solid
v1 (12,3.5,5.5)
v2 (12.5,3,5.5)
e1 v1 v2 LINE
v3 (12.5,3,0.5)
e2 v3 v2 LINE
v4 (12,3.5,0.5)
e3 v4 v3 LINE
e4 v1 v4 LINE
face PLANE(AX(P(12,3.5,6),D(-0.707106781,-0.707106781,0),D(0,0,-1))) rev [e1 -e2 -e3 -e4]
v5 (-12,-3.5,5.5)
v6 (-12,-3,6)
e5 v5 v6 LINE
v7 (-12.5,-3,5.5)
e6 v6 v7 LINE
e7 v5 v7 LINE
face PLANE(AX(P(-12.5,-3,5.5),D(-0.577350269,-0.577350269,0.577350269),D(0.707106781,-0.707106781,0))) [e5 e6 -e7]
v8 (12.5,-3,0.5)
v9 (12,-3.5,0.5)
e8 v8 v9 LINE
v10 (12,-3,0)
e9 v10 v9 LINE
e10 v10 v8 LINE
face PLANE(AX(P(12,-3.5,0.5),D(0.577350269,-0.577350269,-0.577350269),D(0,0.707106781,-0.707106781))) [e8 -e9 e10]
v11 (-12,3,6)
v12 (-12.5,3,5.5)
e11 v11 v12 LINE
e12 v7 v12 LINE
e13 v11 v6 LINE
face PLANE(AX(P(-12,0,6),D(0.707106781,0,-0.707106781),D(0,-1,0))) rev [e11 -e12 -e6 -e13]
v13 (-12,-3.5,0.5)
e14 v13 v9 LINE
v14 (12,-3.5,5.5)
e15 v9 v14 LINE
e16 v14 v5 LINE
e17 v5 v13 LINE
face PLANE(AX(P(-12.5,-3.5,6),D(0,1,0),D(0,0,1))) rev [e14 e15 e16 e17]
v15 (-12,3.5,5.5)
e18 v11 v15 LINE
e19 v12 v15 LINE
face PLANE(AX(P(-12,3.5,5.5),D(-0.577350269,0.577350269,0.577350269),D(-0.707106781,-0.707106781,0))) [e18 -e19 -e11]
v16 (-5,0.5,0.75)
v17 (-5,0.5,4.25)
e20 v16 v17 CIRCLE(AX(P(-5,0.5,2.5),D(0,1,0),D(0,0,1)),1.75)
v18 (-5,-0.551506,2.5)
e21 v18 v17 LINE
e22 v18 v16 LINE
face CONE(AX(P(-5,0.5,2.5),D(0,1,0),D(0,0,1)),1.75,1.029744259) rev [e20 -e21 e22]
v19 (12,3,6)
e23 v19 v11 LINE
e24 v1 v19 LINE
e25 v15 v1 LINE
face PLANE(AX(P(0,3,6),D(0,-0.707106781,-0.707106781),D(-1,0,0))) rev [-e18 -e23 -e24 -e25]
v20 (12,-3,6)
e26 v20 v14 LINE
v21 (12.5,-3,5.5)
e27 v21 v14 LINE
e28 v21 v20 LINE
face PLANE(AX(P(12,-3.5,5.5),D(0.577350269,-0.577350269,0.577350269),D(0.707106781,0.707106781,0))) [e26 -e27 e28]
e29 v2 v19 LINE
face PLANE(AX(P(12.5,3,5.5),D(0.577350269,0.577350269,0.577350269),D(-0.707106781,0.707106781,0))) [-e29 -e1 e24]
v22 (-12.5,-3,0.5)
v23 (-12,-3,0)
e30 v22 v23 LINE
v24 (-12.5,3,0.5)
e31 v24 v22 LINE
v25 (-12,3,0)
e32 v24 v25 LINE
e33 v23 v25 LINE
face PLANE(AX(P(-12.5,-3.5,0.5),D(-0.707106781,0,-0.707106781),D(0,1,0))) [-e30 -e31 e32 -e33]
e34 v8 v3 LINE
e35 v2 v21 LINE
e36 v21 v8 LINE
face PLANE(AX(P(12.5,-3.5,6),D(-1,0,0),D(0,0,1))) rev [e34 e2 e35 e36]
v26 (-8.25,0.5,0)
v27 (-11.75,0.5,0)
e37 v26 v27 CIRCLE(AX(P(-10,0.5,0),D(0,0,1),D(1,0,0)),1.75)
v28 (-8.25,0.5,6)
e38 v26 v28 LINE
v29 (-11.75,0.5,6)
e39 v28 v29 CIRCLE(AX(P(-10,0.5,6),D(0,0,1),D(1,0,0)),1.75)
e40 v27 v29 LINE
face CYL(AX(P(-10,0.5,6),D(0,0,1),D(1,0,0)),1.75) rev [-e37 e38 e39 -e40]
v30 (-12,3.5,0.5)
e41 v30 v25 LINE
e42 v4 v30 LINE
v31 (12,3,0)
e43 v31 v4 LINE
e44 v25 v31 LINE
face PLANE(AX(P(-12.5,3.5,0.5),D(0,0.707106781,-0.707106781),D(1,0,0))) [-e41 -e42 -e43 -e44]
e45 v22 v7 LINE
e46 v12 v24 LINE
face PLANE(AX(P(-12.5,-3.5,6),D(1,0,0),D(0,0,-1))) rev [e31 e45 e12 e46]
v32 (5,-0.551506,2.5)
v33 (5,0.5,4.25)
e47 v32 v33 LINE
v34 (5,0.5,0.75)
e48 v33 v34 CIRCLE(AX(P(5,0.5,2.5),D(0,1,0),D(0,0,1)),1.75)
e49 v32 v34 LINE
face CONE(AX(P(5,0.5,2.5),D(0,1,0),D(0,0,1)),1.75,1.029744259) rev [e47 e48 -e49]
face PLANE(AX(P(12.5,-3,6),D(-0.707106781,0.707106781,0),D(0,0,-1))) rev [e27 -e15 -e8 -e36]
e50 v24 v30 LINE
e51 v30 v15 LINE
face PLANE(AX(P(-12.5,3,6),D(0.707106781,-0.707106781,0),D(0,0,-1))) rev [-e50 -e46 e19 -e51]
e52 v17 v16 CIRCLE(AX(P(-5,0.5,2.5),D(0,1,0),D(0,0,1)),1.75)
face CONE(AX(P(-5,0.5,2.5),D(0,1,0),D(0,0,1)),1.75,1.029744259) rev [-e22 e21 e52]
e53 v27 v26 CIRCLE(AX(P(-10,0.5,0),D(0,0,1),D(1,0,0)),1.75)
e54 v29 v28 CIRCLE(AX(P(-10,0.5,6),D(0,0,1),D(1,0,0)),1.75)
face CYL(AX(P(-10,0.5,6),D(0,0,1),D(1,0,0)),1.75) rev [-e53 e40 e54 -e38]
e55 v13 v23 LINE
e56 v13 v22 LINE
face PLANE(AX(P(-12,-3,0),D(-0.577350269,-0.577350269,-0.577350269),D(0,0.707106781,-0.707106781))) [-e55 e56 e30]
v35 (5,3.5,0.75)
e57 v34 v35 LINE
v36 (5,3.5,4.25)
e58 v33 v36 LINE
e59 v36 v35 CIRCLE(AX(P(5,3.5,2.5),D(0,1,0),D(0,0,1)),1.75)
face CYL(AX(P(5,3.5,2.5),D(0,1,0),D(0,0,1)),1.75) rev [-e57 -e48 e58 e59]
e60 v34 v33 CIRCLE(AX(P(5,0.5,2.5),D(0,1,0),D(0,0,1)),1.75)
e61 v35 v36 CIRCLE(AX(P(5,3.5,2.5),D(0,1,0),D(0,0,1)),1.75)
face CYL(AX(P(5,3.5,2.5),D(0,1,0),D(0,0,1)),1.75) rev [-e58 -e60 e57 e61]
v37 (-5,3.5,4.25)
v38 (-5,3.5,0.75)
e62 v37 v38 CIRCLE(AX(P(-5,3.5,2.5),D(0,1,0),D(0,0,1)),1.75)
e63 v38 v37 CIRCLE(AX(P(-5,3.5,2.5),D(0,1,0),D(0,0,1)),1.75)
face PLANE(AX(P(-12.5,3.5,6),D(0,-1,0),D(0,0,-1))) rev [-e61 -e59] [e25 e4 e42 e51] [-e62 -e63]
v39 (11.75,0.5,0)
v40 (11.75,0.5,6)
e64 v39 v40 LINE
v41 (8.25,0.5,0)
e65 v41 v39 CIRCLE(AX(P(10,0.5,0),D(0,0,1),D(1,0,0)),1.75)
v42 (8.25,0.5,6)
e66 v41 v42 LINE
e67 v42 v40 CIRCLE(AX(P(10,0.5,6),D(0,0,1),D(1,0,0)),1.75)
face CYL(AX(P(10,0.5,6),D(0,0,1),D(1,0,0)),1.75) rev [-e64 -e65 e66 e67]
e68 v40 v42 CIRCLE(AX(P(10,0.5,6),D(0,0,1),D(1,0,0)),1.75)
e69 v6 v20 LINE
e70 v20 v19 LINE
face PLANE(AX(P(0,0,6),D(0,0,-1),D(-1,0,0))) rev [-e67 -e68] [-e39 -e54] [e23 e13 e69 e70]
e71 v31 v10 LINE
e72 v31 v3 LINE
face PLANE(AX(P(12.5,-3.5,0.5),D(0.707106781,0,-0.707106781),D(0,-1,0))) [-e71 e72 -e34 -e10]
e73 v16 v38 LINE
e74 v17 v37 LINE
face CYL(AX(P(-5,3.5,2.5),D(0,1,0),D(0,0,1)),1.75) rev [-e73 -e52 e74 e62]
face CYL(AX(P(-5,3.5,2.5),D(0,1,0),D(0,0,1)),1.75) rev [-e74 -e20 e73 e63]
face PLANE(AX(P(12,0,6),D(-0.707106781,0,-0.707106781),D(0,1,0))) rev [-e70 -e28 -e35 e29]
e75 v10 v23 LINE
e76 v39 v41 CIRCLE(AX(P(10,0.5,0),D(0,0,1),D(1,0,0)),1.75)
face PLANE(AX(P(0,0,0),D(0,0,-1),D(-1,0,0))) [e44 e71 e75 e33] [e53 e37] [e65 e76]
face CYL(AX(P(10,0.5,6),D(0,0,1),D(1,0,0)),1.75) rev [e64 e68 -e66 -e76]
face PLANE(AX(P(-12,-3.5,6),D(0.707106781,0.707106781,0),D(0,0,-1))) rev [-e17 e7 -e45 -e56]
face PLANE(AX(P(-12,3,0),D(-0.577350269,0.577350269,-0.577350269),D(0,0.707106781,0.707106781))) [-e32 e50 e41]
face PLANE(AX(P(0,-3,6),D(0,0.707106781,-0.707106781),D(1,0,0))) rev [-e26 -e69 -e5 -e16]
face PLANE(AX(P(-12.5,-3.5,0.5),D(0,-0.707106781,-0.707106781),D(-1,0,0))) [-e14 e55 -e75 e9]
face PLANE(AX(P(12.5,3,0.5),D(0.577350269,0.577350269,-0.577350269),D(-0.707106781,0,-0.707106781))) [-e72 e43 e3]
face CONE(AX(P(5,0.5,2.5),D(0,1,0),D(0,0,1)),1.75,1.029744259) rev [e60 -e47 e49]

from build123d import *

# Parameters (mm, degrees)
SKETCH1_W                      = 25
SKETCH1_H                      = 7
BOSS_EXTRUDE1_DEPTH            = 6
F_3_5_3_5_DIAMETER_HOLE2_D     = 3.5
F_3_5_3_5_DIAMETER_HOLE3_D     = 3.5
F_3_5_3_5_DIAMETER_HOLE3_DEPTH = 3
F_3_5_3_5_DIAMETER_HOLE3_TIP   = 1.051506083
CHAMFER1_SIZE                  = 0.5


with BuildPart() as part:
    # Sketch1 → Boss-Extrude1 (new body)
    with BuildSketch(Plane.XY):
        Rectangle(SKETCH1_W, SKETCH1_H)
    extrude(amount=BOSS_EXTRUDE1_DEPTH)

    # Ø3.5 (3.5) Diameter Hole2 (through all)
    with Locations(Plane.XY.offset(6)):
        with Locations((-10, 0.5), (10, 0.5)):
            Hole(F_3_5_3_5_DIAMETER_HOLE2_D / 2)

    # Ø3.5 (3.5) Diameter Hole3
    with Locations(Plane(origin=(0, 3.5, 0), x_dir=(1, 0, 0), z_dir=(0, 1, 0))):
        with Locations((5, -2.5), (-5, -2.5)):
            Hole(F_3_5_3_5_DIAMETER_HOLE3_D / 2, depth=F_3_5_3_5_DIAMETER_HOLE3_DEPTH)
            with Locations((0, 0, -(F_3_5_3_5_DIAMETER_HOLE3_DEPTH + F_3_5_3_5_DIAMETER_HOLE3_TIP / 2))):  # 118° drill point
                Cone(0, F_3_5_3_5_DIAMETER_HOLE3_D / 2, F_3_5_3_5_DIAMETER_HOLE3_TIP, mode=Mode.SUBTRACT)

    # Chamfer1
    chamfer1_edges = [part.edges().sort_by_distance(p)[0] for p in [
        (-12.5, 0, 6),
        (0, -3.5, 6),
        (12.5, 0, 6),
        (0, -3.5, 0),
        (-12.5, 0, 0),
        (0, 3.5, 0),
        (12.5, 0, 0),
        (0, 3.5, 6),
        (12.5, -3.5, 3),
        (-12.5, -3.5, 3),
        (-12.5, 3.5, 3),
        (12.5, 3.5, 3),
    ]]
    chamfer(chamfer1_edges, length=CHAMFER1_SIZE)


solid = part.part
